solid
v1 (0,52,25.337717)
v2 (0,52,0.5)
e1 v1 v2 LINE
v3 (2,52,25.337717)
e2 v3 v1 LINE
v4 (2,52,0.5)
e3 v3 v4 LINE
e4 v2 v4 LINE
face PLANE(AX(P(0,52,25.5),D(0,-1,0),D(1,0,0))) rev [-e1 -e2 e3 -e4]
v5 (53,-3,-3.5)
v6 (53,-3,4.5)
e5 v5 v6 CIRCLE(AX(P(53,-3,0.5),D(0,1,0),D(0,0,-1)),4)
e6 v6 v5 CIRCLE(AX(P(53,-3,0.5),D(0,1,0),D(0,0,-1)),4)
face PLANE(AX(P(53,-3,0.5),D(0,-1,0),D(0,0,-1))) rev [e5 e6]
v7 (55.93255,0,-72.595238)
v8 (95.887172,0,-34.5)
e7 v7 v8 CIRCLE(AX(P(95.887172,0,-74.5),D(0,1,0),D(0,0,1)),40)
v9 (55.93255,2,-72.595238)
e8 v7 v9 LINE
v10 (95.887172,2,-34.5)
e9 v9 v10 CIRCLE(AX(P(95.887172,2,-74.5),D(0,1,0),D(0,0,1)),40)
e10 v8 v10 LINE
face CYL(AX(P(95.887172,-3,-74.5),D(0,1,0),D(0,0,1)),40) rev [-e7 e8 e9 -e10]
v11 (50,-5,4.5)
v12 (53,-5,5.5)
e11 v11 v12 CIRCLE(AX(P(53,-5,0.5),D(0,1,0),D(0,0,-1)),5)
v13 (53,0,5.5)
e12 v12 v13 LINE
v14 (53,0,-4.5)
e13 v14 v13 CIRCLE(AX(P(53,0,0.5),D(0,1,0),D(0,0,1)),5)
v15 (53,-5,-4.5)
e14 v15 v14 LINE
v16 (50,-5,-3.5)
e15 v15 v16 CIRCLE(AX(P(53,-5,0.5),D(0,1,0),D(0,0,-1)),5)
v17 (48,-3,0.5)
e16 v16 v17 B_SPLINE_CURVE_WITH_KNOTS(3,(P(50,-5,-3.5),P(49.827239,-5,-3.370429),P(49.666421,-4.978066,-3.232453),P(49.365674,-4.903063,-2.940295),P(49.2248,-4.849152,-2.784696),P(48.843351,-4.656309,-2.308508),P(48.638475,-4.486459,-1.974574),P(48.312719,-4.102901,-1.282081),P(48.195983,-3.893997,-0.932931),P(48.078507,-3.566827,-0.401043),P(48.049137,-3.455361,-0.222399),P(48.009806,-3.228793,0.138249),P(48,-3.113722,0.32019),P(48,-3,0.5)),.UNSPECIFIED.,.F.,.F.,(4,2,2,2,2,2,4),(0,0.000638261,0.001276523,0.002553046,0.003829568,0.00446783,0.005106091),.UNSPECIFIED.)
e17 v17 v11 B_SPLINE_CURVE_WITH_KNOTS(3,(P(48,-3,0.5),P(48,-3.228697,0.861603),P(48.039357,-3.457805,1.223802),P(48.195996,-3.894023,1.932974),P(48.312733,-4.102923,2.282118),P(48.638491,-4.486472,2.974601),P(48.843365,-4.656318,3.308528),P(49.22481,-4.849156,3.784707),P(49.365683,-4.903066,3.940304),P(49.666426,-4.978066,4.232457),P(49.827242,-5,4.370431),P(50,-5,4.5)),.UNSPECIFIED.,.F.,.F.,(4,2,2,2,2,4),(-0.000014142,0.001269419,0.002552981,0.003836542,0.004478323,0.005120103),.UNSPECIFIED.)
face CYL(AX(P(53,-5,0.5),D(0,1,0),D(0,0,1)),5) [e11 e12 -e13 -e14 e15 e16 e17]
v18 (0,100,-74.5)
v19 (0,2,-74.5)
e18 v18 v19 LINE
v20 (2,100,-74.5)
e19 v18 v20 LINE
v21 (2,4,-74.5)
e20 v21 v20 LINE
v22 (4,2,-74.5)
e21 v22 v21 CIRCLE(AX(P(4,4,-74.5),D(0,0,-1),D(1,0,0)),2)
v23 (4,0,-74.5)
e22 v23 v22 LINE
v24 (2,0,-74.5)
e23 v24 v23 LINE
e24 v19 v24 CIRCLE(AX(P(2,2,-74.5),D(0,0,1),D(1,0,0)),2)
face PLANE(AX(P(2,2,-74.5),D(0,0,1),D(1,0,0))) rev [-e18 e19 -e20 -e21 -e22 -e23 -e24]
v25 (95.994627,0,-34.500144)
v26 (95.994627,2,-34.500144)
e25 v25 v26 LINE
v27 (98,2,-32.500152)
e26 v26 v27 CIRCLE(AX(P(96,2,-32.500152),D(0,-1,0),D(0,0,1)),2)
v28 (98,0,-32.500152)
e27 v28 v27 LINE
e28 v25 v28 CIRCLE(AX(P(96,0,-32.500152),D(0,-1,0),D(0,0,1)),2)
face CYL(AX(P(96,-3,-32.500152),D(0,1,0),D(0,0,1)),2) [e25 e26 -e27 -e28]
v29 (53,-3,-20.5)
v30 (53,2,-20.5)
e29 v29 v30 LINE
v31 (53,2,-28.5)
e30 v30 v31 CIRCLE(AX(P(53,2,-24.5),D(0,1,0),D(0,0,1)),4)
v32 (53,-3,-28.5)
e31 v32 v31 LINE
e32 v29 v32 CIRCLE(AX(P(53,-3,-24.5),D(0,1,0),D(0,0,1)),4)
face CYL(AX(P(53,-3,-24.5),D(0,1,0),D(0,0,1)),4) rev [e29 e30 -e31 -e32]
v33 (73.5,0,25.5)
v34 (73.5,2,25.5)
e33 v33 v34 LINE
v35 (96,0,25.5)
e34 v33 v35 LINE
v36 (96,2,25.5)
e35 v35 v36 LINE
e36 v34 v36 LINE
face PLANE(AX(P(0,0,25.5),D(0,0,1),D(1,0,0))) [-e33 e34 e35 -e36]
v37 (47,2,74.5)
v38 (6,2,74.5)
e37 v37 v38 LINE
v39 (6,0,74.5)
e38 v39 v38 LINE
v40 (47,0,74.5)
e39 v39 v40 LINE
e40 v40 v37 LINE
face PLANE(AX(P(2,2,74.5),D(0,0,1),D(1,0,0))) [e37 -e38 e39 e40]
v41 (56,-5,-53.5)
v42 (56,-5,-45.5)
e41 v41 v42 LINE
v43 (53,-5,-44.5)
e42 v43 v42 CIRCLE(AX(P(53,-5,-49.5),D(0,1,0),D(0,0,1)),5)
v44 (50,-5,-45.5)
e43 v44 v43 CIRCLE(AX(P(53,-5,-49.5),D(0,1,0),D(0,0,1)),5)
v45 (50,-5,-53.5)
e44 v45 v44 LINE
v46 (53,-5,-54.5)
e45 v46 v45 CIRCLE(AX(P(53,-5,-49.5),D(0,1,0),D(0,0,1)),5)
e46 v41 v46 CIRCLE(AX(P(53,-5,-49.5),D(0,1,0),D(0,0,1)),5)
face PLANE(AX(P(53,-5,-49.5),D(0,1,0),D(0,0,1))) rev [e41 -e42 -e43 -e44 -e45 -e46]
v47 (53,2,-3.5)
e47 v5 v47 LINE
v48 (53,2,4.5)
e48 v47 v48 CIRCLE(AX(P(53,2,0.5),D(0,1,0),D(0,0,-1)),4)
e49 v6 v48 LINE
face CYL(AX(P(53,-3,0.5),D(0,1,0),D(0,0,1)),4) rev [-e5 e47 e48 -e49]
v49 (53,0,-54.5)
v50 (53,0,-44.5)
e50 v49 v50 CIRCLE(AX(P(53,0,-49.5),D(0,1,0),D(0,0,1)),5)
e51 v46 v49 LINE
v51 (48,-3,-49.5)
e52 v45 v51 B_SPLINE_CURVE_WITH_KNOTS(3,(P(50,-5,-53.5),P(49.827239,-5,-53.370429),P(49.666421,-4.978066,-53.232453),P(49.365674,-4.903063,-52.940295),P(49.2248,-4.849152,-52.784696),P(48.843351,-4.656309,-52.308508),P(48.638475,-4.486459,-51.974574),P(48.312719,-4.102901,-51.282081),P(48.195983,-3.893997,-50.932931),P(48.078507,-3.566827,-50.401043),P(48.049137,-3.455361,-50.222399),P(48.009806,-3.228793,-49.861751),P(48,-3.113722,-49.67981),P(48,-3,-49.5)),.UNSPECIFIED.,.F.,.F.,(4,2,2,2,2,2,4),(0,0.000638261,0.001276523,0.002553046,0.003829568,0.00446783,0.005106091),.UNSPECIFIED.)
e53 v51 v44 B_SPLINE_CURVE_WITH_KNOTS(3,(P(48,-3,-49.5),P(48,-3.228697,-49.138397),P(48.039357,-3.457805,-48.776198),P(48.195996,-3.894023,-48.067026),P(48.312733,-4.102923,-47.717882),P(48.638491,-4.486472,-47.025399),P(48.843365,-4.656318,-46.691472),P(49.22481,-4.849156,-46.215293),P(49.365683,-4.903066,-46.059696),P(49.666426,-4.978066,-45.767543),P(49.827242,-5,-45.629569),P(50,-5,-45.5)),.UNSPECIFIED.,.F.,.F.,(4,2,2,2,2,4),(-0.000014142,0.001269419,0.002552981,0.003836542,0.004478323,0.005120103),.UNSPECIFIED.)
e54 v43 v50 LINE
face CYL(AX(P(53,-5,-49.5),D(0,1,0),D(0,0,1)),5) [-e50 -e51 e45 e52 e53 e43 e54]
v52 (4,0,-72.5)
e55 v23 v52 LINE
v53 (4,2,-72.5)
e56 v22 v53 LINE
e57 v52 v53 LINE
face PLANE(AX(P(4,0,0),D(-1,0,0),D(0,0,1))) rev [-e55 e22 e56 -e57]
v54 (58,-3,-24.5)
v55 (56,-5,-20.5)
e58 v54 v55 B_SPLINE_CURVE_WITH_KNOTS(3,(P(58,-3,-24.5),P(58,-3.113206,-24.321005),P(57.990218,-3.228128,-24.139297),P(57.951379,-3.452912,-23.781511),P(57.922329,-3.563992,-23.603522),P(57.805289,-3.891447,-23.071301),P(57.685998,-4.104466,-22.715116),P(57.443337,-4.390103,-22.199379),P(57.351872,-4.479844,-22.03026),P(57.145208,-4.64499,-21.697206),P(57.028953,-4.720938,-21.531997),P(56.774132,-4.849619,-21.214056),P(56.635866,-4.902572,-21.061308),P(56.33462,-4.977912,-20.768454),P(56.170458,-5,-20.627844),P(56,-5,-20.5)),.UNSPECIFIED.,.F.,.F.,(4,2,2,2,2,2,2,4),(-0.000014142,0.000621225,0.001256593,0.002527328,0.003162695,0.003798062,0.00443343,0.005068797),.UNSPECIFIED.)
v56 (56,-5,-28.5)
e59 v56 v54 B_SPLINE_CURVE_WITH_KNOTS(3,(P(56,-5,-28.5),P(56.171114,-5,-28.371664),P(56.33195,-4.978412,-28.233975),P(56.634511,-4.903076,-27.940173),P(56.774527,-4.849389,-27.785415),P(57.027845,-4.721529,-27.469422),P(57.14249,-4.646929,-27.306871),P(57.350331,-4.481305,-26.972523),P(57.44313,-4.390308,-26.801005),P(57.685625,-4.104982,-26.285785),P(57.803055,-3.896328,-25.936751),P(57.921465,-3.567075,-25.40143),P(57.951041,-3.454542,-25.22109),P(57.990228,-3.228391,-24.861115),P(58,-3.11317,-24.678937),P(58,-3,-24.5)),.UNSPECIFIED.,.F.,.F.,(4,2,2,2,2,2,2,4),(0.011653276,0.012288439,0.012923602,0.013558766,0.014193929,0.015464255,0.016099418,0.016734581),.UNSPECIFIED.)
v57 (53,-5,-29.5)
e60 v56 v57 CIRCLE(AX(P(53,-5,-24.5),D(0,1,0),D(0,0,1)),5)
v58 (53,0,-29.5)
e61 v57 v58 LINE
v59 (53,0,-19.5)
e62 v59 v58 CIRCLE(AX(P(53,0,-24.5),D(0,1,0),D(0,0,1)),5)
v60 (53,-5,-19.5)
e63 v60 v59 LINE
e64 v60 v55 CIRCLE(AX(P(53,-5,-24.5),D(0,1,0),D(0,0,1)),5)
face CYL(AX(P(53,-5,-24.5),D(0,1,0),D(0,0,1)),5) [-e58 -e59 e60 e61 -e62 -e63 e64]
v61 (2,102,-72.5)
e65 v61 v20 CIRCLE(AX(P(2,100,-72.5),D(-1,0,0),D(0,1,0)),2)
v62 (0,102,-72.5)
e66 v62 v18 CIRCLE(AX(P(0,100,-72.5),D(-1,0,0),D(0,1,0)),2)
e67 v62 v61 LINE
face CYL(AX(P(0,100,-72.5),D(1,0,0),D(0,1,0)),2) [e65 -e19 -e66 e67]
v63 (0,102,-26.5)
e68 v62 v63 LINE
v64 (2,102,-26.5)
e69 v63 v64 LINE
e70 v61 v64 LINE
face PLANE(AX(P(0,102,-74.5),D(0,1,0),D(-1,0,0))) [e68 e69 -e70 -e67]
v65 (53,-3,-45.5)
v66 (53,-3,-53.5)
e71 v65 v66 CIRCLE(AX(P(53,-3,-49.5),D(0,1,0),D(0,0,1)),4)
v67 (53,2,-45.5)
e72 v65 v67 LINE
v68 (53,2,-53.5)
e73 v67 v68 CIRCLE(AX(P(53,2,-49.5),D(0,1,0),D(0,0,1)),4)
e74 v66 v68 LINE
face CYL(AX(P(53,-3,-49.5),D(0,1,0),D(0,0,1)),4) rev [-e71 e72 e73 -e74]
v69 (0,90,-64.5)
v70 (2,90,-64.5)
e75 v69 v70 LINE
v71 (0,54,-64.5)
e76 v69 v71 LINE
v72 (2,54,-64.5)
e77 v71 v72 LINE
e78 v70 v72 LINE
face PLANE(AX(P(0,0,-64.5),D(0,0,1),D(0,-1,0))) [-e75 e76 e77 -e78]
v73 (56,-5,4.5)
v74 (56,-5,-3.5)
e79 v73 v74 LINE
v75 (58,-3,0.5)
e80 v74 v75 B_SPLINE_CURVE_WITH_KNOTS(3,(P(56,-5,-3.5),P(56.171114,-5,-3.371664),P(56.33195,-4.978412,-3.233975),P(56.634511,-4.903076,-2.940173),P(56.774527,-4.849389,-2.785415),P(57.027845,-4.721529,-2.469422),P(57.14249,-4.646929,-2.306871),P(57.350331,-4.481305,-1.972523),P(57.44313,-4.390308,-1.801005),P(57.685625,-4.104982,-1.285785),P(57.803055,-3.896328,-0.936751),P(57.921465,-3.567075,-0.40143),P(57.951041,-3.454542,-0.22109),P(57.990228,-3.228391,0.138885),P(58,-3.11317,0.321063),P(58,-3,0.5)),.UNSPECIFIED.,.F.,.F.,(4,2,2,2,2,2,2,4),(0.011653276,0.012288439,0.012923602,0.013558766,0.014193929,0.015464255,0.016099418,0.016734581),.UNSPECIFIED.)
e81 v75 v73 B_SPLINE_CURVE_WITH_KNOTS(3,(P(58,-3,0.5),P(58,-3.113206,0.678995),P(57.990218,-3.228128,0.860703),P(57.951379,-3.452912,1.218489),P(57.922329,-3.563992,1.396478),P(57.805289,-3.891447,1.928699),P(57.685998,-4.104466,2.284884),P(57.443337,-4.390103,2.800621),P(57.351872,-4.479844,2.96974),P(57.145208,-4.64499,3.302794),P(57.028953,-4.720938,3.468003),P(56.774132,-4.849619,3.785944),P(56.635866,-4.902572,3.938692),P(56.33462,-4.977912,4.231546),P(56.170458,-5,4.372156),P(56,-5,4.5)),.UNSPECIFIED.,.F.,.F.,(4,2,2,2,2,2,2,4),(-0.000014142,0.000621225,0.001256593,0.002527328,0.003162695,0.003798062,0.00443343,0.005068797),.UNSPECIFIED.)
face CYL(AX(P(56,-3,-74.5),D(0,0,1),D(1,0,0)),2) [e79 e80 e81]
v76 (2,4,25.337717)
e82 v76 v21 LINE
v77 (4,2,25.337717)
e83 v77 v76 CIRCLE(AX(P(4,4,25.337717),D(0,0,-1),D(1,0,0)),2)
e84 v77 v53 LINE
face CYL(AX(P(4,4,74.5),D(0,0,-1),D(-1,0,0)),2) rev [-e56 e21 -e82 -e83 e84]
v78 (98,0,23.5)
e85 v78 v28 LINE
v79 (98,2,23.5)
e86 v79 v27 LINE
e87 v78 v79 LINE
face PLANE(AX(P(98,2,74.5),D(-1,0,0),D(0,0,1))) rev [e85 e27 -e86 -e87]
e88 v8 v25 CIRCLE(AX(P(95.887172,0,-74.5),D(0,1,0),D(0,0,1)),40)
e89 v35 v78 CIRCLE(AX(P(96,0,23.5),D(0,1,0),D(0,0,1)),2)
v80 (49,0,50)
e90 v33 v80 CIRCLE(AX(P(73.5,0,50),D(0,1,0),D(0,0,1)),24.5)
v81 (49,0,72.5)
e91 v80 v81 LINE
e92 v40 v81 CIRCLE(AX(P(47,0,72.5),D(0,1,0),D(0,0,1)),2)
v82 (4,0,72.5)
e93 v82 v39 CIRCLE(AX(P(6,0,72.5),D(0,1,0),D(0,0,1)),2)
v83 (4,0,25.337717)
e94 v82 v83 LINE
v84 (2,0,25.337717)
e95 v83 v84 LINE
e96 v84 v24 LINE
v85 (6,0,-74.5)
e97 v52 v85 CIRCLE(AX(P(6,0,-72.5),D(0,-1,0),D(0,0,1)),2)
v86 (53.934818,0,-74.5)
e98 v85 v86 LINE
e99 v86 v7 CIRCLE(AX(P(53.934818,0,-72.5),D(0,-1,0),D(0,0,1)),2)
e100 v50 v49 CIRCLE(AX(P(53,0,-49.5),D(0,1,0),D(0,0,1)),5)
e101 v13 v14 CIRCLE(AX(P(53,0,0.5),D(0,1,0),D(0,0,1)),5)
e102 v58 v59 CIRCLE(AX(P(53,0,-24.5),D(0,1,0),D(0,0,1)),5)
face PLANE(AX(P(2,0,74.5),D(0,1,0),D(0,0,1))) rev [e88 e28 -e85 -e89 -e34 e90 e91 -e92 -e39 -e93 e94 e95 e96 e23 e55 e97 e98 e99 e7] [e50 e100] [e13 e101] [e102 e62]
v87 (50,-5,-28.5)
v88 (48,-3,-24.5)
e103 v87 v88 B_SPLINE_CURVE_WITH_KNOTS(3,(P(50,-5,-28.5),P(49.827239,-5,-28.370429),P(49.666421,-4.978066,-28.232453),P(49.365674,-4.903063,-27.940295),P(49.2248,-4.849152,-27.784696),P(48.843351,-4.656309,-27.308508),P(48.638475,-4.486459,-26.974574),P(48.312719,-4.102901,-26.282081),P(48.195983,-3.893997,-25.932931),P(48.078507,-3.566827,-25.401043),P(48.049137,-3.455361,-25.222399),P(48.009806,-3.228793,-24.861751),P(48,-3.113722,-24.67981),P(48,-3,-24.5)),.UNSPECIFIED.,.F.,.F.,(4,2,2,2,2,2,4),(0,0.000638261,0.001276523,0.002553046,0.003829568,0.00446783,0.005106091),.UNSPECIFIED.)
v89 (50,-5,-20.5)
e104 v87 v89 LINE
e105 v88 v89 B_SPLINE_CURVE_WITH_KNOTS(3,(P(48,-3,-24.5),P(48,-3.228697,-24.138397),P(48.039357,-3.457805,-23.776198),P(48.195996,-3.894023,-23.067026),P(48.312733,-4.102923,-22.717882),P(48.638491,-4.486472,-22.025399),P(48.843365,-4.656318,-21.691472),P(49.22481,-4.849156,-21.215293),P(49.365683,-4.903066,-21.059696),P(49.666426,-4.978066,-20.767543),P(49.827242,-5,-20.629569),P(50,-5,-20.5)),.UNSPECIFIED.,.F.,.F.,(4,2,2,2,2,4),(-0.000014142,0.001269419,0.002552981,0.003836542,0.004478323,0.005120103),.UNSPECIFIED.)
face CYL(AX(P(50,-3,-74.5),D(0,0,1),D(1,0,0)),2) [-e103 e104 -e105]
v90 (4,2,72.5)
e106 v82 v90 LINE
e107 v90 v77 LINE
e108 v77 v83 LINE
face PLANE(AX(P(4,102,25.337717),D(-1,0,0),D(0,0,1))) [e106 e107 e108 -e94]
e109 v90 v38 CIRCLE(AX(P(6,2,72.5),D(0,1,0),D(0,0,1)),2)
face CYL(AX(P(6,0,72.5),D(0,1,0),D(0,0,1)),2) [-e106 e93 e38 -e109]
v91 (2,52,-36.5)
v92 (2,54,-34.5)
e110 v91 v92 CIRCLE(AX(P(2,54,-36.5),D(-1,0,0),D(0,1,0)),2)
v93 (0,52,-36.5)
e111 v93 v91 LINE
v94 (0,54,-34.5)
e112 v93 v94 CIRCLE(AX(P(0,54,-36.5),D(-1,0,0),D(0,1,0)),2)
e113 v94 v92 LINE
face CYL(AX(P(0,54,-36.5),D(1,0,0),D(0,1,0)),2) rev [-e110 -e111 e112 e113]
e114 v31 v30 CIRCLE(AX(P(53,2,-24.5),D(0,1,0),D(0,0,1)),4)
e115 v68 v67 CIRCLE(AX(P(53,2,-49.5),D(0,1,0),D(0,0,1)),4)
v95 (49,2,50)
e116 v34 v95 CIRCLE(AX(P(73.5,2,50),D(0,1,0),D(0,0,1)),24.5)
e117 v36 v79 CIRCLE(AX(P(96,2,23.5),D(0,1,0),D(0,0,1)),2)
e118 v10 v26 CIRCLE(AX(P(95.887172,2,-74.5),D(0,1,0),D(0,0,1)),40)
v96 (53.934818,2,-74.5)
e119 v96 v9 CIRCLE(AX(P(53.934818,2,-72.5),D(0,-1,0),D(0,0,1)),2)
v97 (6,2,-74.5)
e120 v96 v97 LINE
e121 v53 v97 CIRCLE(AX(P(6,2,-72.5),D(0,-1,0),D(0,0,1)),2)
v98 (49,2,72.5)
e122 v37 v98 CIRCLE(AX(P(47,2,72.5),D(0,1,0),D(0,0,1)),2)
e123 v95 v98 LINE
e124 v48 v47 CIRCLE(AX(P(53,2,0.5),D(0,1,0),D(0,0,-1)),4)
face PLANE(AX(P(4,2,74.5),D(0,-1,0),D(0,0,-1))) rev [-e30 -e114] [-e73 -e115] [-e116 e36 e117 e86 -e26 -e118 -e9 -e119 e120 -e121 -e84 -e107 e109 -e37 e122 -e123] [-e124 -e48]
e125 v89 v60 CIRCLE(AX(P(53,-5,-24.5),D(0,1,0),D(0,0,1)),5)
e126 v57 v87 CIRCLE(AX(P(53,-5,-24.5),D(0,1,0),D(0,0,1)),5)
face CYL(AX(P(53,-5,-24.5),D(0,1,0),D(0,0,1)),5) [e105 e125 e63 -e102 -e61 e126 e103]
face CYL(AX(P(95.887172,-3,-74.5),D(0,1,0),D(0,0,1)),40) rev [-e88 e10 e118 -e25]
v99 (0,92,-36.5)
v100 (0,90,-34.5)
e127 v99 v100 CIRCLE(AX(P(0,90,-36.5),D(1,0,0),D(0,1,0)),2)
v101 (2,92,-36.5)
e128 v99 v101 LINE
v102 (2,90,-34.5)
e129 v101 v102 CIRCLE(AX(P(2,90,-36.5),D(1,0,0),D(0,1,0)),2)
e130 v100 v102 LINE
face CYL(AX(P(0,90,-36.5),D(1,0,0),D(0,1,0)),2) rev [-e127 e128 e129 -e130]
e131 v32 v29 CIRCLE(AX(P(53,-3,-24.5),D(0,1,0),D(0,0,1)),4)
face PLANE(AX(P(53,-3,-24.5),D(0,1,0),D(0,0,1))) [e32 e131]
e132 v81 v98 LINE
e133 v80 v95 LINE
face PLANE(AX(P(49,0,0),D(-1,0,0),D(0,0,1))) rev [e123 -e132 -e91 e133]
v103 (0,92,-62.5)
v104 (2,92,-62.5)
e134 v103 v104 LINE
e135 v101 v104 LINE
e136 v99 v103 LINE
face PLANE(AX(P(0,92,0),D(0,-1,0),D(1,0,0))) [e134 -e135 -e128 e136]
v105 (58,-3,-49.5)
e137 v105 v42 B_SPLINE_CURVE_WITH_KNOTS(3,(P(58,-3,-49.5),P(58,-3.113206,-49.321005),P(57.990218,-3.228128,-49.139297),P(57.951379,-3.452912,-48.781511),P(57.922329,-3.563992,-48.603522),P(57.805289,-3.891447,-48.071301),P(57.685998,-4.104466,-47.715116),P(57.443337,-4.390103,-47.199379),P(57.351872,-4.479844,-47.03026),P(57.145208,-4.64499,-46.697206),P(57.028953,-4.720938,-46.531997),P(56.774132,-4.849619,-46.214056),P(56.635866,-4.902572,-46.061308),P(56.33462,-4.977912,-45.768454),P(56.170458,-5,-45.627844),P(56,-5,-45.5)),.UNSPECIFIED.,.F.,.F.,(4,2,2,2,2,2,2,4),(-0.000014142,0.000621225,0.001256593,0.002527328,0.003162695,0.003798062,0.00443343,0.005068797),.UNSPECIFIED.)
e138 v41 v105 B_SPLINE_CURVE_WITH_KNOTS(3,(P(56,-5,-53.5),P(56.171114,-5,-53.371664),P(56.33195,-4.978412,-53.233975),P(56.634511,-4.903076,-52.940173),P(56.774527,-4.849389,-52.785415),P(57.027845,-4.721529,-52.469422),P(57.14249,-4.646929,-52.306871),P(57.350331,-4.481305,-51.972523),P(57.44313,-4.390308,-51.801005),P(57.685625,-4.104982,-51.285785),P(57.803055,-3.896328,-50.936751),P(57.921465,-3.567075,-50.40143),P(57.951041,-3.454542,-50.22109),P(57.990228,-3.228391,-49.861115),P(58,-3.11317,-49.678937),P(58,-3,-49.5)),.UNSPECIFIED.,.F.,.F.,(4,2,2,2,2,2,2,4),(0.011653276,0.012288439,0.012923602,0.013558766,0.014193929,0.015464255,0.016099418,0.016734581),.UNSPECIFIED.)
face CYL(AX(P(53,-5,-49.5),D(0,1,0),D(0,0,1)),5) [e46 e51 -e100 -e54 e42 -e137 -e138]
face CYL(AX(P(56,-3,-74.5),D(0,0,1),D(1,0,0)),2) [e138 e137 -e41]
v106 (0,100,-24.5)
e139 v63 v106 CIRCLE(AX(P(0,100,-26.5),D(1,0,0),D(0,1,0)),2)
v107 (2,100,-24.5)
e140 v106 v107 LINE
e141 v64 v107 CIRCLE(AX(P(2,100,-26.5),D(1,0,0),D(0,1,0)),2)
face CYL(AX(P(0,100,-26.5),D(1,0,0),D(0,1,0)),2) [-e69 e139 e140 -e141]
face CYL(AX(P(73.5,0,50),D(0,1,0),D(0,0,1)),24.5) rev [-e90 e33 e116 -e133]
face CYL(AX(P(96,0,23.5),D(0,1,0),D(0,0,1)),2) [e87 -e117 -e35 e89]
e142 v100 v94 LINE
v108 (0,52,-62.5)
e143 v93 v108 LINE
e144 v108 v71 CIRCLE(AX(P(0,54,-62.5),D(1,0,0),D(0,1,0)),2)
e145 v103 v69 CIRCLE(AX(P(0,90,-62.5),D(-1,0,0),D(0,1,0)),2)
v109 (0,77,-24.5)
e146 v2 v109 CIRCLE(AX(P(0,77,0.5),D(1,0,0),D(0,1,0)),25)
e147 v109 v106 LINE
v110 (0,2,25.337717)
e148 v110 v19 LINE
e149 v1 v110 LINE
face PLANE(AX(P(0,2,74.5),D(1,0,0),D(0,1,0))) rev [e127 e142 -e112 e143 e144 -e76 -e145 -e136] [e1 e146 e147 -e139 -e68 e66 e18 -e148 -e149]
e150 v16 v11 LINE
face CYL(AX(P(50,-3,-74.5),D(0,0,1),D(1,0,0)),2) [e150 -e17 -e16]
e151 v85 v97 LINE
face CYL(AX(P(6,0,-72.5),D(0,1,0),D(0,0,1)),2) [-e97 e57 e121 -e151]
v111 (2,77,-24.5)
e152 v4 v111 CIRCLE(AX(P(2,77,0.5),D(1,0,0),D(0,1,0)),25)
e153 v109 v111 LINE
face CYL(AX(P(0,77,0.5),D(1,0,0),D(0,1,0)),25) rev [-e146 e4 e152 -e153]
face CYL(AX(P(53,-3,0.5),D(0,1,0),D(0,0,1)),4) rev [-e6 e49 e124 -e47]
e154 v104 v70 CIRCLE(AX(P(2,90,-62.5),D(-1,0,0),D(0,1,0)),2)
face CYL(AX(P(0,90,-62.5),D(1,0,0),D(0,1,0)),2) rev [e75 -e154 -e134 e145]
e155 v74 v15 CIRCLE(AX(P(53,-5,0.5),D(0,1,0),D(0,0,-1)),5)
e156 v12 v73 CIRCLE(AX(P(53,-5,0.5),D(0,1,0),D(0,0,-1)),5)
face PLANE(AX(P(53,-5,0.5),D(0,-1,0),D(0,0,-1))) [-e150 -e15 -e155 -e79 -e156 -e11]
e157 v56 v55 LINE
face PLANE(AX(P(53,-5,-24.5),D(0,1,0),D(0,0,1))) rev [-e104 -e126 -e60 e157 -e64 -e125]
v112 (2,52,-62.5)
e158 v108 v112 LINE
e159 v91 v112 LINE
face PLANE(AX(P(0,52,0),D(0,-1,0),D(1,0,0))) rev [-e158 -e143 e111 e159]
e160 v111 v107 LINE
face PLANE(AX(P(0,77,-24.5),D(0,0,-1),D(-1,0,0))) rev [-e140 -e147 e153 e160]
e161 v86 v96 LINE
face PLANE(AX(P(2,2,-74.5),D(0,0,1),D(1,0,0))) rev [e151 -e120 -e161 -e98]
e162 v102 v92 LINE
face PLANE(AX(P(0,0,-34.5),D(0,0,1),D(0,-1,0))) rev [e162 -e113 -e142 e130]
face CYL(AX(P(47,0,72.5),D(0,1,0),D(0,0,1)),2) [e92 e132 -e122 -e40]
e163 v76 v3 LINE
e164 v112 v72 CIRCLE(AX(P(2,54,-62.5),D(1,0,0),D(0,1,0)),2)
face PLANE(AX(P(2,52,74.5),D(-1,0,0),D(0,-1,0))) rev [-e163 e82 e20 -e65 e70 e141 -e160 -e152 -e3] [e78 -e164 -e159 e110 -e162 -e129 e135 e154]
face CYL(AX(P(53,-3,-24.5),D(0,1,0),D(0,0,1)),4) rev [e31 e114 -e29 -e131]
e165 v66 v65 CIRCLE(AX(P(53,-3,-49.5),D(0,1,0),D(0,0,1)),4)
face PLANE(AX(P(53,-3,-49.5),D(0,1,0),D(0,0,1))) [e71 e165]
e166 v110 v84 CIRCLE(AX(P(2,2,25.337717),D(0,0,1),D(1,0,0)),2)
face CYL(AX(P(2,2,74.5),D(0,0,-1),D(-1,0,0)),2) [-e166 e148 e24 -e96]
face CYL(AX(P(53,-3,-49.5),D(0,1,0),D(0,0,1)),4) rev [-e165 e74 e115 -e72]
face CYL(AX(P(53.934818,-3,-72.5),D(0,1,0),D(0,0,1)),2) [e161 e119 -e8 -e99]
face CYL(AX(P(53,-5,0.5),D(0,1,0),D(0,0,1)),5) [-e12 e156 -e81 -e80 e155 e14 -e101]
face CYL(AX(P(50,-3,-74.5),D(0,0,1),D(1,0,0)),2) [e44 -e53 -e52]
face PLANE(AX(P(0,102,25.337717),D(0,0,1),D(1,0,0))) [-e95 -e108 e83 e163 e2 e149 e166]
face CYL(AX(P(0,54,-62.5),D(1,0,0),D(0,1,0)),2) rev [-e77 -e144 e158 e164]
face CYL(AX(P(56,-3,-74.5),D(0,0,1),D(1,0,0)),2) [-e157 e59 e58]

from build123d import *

# Parameters (mm, degrees)
L_SECTION_BRACKET_BODY_149MM_DEPTH = 74.5
FLANGE_TAB_SKETCH_W                = 149
FLANGE_TAB_SKETCH_H                = 50
FLANGE_TAB_2MM_DEPTH               = 2
UPRIGHT_RADIUS_OUTLINE_CUT_DEPTH   = 2
TRIM_CUT_DEPTH                     = 159.600914247
TRIM_CUT_DEPTH_BACK                = 159.600914247
TRIM_CUT_SKETCH_W                  = 4
TRIM_CUT_SKETCH_H                  = 49.162283459
UPRIGHT_WINDOW_CUT_DEPTH           = 2
BASE_OUTLINE_CUT_DEPTH             = 2
BASE_BOSS_SKETCH_R                 = 5
BASE_BOSS_7MM_DEPTH                = 7
BASE_BOSS_RELIEF_CUT_DEPTH         = 160.869478013
BASE_BOSS_RELIEF_CUT_DEPTH_BACK    = 160.869478013
BASE_HOLE_SKETCH_R                 = 4
BASE_HOLE_CUT_DEPTH                = 5
BASE_RADIUS_NOTCH_CUT_DEPTH        = 5


with BuildPart() as part:
    # L-Section Profile Sketch → L-Section Bracket Body 149mm (new, symmetric)
    with BuildSketch(Plane.XY):
        with BuildLine():
            Line((2, 0), (98, 0))
            Line((98, 0), (98, 2))
            Line((98, 2), (4, 2))
            ThreePointArc((4, 2), (2.585786438, 2.585786438), (2, 4))
            Line((2, 4), (2, 52))
            Line((2, 52), (0, 52))
            Line((0, 52), (0, 2))
            ThreePointArc((0, 2), (0.585786438, 0.585786438), (2, 0))
        make_face()
    extrude(amount=L_SECTION_BRACKET_BODY_149MM_DEPTH, both=True)

    # Flange Tab Sketch → Flange Tab 2mm (add)
    with BuildSketch(Plane(origin=(2, 0, 0), x_dir=(0, 0, -1), z_dir=(1, 0, 0))):
        with Locations((0, 77)):
            Rectangle(FLANGE_TAB_SKETCH_W, FLANGE_TAB_SKETCH_H)
    extrude(amount=-FLANGE_TAB_2MM_DEPTH)

    # Upright Radius Outline Sketch → Upright Radius Outline Cut (cut)
    with BuildSketch(Plane(origin=(2, 0, 0), x_dir=(0, 0, -1), z_dir=(1, 0, 0))):
        with BuildLine():
            Line((24.5, 102), (-74.5, 102))
            Line((-74.5, 102), (-74.5, 4))
            Line((-74.5, 4), (-25.5, 4))
            Line((-25.5, 4), (-25.5, 52))
            Line((-25.5, 52), (-0.5, 52))
            ThreePointArc((-0.5, 52), (17.17766953, 59.32233047), (24.5, 77))
            Line((24.5, 77), (24.5, 102))
        make_face()
    extrude(amount=-UPRIGHT_RADIUS_OUTLINE_CUT_DEPTH, mode=Mode.SUBTRACT)

    # Trim Cut Sketch → Trim Cut (cut, two sides: drawn at the far end of the back side and taken through both)
    with BuildSketch(Plane(origin=(0, 2, 0), x_dir=(1, 0, 0), z_dir=(0, 1, 0)).offset(-TRIM_CUT_DEPTH_BACK)):
        with Locations((2, -49.918858271)):
            Rectangle(TRIM_CUT_SKETCH_W, TRIM_CUT_SKETCH_H)
    extrude(amount=TRIM_CUT_DEPTH + TRIM_CUT_DEPTH_BACK, mode=Mode.SUBTRACT)

    # Upright Window Sketch → Upright Window Cut (cut)
    with BuildSketch(Plane(origin=(2, 0, 0), x_dir=(0, 0, -1), z_dir=(1, 0, 0))):
        with BuildLine():
            ThreePointArc((24.5, 100), (25.085786438, 101.414213562), (26.5, 102))
            Line((26.5, 102), (24.5, 102))
            Line((24.5, 102), (24.5, 100))
        make_face()
        with BuildLine():
            Line((74.5, 100), (74.5, 102))
            Line((74.5, 102), (72.5, 102))
            ThreePointArc((72.5, 102), (73.914213562, 101.414213562), (74.5, 100))
        make_face()
        with BuildLine():
            ThreePointArc((36.5, 52), (35.085786438, 52.585786438), (34.5, 54))
            Line((34.5, 54), (34.5, 90))
            ThreePointArc((34.5, 90), (35.085786438, 91.414213562), (36.5, 92))
            Line((36.5, 92), (62.5, 92))
            ThreePointArc((62.5, 92), (63.914213562, 91.414213562), (64.5, 90))
            Line((64.5, 90), (64.5, 54))
            ThreePointArc((64.5, 54), (63.914213562, 52.585786438), (62.5, 52))
            Line((62.5, 52), (36.5, 52))
        make_face()
    extrude(amount=-UPRIGHT_WINDOW_CUT_DEPTH, mode=Mode.SUBTRACT)

    # Base Outline Sketch → Base Outline Cut (cut)
    with BuildSketch(Plane(origin=(0, 2, 0), x_dir=(1, 0, 0), z_dir=(0, 1, 0))):
        with BuildLine():
            Line((6, 74.5), (4, 74.5))
            Line((4, 74.5), (4, 72.5))
            ThreePointArc((4, 72.5), (4.585786438, 73.914213562), (6, 74.5))
        make_face()
        with BuildLine():
            Line((98, -74.5), (98, -23.5))
            ThreePointArc((98, -23.5), (97.414213562, -24.914213562), (96, -25.5))
            Line((96, -25.5), (73.5, -25.5))
            ThreePointArc((73.5, -25.5), (56.175883861, -32.675883861), (49, -50))
            Line((49, -50), (49, -72.5))
            ThreePointArc((49, -72.5), (48.414213562, -73.914213562), (47, -74.5))
            Line((47, -74.5), (98, -74.5))
        make_face()
        with BuildLine():
            ThreePointArc((6, -74.5), (4.585786438, -73.914213562), (4, -72.5))
            Line((4, -72.5), (4, -74.5))
            Line((4, -74.5), (6, -74.5))
        make_face()
    extrude(amount=-BASE_OUTLINE_CUT_DEPTH, mode=Mode.SUBTRACT)

    # Base Boss Sketch → Base Boss 7mm (add)
    with BuildSketch(Plane(origin=(0, 2, 0), x_dir=(1, 0, 0), z_dir=(0, 1, 0))):
        with Locations(Location((53, 24.5, 0), (0, 0, 270))):
            Circle(BASE_BOSS_SKETCH_R)
        with Locations(Location((53, 49.5, 0), (0, 0, 270))):
            Circle(BASE_BOSS_SKETCH_R)
        with Locations(Location((53, -0.5, 0), (0, 0, 270))):
            Circle(BASE_BOSS_SKETCH_R)
    extrude(amount=-BASE_BOSS_7MM_DEPTH)

    # Base Boss Relief Sketch → Base Boss Relief Cut (cut, two sides: drawn at the far end of the back side and taken through both)
    with BuildSketch(Plane.XY.offset(-BASE_BOSS_RELIEF_CUT_DEPTH_BACK)):
        with BuildLine():
            ThreePointArc((48, -3), (48.585786438, -4.414213562), (50, -5))
            Line((50, -5), (48, -5))
            Line((48, -5), (48, -3))
        make_face()
        with BuildLine():
            Line((58, -3), (58, -5))
            Line((58, -5), (56, -5))
            ThreePointArc((56, -5), (57.414213562, -4.414213562), (58, -3))
        make_face()
    extrude(amount=BASE_BOSS_RELIEF_CUT_DEPTH + BASE_BOSS_RELIEF_CUT_DEPTH_BACK, mode=Mode.SUBTRACT)

    # Base Hole Sketch → Base Hole Cut (cut)
    with BuildSketch(Plane(origin=(0, 2, 0), x_dir=(1, 0, 0), z_dir=(0, 1, 0))):
        with Locations(Location((53, 24.5, 0), (0, 0, 270))):
            Circle(BASE_HOLE_SKETCH_R)
        with Locations(Location((53, 49.5, 0), (0, 0, 270))):
            Circle(BASE_HOLE_SKETCH_R)
        with Locations(Location((53, -0.5, 0), (0, 0, 90))):
            Circle(BASE_HOLE_SKETCH_R)
    extrude(amount=-BASE_HOLE_CUT_DEPTH, mode=Mode.SUBTRACT)

    # Base Radius Notch Sketch → Base Radius Notch Cut (cut)
    with BuildSketch(Plane(origin=(0, 2, 0), x_dir=(1, 0, 0), z_dir=(0, 1, 0))):
        with BuildLine():
            Line((55.887172383, 74.5), (53.934818456, 74.5))
            ThreePointArc((53.934818456, 74.5), (55.314949575, 73.947493729), (55.932549596, 72.595238095))
            ThreePointArc((55.932549596, 72.595238095), (68.323460008, 45.51307605), (95.994627256, 34.500144332))
            ThreePointArc((95.994627256, 34.500144332), (97.412312733, 33.916263389), (98, 32.500151549))
            Line((98, 32.500151549), (98, 34.555839482))
            Line((98, 34.555839482), (98, 74.5))
            Line((98, 74.5), (55.887172383, 74.5))
        make_face()
    extrude(amount=-BASE_RADIUS_NOTCH_CUT_DEPTH, mode=Mode.SUBTRACT)


solid = part.part
